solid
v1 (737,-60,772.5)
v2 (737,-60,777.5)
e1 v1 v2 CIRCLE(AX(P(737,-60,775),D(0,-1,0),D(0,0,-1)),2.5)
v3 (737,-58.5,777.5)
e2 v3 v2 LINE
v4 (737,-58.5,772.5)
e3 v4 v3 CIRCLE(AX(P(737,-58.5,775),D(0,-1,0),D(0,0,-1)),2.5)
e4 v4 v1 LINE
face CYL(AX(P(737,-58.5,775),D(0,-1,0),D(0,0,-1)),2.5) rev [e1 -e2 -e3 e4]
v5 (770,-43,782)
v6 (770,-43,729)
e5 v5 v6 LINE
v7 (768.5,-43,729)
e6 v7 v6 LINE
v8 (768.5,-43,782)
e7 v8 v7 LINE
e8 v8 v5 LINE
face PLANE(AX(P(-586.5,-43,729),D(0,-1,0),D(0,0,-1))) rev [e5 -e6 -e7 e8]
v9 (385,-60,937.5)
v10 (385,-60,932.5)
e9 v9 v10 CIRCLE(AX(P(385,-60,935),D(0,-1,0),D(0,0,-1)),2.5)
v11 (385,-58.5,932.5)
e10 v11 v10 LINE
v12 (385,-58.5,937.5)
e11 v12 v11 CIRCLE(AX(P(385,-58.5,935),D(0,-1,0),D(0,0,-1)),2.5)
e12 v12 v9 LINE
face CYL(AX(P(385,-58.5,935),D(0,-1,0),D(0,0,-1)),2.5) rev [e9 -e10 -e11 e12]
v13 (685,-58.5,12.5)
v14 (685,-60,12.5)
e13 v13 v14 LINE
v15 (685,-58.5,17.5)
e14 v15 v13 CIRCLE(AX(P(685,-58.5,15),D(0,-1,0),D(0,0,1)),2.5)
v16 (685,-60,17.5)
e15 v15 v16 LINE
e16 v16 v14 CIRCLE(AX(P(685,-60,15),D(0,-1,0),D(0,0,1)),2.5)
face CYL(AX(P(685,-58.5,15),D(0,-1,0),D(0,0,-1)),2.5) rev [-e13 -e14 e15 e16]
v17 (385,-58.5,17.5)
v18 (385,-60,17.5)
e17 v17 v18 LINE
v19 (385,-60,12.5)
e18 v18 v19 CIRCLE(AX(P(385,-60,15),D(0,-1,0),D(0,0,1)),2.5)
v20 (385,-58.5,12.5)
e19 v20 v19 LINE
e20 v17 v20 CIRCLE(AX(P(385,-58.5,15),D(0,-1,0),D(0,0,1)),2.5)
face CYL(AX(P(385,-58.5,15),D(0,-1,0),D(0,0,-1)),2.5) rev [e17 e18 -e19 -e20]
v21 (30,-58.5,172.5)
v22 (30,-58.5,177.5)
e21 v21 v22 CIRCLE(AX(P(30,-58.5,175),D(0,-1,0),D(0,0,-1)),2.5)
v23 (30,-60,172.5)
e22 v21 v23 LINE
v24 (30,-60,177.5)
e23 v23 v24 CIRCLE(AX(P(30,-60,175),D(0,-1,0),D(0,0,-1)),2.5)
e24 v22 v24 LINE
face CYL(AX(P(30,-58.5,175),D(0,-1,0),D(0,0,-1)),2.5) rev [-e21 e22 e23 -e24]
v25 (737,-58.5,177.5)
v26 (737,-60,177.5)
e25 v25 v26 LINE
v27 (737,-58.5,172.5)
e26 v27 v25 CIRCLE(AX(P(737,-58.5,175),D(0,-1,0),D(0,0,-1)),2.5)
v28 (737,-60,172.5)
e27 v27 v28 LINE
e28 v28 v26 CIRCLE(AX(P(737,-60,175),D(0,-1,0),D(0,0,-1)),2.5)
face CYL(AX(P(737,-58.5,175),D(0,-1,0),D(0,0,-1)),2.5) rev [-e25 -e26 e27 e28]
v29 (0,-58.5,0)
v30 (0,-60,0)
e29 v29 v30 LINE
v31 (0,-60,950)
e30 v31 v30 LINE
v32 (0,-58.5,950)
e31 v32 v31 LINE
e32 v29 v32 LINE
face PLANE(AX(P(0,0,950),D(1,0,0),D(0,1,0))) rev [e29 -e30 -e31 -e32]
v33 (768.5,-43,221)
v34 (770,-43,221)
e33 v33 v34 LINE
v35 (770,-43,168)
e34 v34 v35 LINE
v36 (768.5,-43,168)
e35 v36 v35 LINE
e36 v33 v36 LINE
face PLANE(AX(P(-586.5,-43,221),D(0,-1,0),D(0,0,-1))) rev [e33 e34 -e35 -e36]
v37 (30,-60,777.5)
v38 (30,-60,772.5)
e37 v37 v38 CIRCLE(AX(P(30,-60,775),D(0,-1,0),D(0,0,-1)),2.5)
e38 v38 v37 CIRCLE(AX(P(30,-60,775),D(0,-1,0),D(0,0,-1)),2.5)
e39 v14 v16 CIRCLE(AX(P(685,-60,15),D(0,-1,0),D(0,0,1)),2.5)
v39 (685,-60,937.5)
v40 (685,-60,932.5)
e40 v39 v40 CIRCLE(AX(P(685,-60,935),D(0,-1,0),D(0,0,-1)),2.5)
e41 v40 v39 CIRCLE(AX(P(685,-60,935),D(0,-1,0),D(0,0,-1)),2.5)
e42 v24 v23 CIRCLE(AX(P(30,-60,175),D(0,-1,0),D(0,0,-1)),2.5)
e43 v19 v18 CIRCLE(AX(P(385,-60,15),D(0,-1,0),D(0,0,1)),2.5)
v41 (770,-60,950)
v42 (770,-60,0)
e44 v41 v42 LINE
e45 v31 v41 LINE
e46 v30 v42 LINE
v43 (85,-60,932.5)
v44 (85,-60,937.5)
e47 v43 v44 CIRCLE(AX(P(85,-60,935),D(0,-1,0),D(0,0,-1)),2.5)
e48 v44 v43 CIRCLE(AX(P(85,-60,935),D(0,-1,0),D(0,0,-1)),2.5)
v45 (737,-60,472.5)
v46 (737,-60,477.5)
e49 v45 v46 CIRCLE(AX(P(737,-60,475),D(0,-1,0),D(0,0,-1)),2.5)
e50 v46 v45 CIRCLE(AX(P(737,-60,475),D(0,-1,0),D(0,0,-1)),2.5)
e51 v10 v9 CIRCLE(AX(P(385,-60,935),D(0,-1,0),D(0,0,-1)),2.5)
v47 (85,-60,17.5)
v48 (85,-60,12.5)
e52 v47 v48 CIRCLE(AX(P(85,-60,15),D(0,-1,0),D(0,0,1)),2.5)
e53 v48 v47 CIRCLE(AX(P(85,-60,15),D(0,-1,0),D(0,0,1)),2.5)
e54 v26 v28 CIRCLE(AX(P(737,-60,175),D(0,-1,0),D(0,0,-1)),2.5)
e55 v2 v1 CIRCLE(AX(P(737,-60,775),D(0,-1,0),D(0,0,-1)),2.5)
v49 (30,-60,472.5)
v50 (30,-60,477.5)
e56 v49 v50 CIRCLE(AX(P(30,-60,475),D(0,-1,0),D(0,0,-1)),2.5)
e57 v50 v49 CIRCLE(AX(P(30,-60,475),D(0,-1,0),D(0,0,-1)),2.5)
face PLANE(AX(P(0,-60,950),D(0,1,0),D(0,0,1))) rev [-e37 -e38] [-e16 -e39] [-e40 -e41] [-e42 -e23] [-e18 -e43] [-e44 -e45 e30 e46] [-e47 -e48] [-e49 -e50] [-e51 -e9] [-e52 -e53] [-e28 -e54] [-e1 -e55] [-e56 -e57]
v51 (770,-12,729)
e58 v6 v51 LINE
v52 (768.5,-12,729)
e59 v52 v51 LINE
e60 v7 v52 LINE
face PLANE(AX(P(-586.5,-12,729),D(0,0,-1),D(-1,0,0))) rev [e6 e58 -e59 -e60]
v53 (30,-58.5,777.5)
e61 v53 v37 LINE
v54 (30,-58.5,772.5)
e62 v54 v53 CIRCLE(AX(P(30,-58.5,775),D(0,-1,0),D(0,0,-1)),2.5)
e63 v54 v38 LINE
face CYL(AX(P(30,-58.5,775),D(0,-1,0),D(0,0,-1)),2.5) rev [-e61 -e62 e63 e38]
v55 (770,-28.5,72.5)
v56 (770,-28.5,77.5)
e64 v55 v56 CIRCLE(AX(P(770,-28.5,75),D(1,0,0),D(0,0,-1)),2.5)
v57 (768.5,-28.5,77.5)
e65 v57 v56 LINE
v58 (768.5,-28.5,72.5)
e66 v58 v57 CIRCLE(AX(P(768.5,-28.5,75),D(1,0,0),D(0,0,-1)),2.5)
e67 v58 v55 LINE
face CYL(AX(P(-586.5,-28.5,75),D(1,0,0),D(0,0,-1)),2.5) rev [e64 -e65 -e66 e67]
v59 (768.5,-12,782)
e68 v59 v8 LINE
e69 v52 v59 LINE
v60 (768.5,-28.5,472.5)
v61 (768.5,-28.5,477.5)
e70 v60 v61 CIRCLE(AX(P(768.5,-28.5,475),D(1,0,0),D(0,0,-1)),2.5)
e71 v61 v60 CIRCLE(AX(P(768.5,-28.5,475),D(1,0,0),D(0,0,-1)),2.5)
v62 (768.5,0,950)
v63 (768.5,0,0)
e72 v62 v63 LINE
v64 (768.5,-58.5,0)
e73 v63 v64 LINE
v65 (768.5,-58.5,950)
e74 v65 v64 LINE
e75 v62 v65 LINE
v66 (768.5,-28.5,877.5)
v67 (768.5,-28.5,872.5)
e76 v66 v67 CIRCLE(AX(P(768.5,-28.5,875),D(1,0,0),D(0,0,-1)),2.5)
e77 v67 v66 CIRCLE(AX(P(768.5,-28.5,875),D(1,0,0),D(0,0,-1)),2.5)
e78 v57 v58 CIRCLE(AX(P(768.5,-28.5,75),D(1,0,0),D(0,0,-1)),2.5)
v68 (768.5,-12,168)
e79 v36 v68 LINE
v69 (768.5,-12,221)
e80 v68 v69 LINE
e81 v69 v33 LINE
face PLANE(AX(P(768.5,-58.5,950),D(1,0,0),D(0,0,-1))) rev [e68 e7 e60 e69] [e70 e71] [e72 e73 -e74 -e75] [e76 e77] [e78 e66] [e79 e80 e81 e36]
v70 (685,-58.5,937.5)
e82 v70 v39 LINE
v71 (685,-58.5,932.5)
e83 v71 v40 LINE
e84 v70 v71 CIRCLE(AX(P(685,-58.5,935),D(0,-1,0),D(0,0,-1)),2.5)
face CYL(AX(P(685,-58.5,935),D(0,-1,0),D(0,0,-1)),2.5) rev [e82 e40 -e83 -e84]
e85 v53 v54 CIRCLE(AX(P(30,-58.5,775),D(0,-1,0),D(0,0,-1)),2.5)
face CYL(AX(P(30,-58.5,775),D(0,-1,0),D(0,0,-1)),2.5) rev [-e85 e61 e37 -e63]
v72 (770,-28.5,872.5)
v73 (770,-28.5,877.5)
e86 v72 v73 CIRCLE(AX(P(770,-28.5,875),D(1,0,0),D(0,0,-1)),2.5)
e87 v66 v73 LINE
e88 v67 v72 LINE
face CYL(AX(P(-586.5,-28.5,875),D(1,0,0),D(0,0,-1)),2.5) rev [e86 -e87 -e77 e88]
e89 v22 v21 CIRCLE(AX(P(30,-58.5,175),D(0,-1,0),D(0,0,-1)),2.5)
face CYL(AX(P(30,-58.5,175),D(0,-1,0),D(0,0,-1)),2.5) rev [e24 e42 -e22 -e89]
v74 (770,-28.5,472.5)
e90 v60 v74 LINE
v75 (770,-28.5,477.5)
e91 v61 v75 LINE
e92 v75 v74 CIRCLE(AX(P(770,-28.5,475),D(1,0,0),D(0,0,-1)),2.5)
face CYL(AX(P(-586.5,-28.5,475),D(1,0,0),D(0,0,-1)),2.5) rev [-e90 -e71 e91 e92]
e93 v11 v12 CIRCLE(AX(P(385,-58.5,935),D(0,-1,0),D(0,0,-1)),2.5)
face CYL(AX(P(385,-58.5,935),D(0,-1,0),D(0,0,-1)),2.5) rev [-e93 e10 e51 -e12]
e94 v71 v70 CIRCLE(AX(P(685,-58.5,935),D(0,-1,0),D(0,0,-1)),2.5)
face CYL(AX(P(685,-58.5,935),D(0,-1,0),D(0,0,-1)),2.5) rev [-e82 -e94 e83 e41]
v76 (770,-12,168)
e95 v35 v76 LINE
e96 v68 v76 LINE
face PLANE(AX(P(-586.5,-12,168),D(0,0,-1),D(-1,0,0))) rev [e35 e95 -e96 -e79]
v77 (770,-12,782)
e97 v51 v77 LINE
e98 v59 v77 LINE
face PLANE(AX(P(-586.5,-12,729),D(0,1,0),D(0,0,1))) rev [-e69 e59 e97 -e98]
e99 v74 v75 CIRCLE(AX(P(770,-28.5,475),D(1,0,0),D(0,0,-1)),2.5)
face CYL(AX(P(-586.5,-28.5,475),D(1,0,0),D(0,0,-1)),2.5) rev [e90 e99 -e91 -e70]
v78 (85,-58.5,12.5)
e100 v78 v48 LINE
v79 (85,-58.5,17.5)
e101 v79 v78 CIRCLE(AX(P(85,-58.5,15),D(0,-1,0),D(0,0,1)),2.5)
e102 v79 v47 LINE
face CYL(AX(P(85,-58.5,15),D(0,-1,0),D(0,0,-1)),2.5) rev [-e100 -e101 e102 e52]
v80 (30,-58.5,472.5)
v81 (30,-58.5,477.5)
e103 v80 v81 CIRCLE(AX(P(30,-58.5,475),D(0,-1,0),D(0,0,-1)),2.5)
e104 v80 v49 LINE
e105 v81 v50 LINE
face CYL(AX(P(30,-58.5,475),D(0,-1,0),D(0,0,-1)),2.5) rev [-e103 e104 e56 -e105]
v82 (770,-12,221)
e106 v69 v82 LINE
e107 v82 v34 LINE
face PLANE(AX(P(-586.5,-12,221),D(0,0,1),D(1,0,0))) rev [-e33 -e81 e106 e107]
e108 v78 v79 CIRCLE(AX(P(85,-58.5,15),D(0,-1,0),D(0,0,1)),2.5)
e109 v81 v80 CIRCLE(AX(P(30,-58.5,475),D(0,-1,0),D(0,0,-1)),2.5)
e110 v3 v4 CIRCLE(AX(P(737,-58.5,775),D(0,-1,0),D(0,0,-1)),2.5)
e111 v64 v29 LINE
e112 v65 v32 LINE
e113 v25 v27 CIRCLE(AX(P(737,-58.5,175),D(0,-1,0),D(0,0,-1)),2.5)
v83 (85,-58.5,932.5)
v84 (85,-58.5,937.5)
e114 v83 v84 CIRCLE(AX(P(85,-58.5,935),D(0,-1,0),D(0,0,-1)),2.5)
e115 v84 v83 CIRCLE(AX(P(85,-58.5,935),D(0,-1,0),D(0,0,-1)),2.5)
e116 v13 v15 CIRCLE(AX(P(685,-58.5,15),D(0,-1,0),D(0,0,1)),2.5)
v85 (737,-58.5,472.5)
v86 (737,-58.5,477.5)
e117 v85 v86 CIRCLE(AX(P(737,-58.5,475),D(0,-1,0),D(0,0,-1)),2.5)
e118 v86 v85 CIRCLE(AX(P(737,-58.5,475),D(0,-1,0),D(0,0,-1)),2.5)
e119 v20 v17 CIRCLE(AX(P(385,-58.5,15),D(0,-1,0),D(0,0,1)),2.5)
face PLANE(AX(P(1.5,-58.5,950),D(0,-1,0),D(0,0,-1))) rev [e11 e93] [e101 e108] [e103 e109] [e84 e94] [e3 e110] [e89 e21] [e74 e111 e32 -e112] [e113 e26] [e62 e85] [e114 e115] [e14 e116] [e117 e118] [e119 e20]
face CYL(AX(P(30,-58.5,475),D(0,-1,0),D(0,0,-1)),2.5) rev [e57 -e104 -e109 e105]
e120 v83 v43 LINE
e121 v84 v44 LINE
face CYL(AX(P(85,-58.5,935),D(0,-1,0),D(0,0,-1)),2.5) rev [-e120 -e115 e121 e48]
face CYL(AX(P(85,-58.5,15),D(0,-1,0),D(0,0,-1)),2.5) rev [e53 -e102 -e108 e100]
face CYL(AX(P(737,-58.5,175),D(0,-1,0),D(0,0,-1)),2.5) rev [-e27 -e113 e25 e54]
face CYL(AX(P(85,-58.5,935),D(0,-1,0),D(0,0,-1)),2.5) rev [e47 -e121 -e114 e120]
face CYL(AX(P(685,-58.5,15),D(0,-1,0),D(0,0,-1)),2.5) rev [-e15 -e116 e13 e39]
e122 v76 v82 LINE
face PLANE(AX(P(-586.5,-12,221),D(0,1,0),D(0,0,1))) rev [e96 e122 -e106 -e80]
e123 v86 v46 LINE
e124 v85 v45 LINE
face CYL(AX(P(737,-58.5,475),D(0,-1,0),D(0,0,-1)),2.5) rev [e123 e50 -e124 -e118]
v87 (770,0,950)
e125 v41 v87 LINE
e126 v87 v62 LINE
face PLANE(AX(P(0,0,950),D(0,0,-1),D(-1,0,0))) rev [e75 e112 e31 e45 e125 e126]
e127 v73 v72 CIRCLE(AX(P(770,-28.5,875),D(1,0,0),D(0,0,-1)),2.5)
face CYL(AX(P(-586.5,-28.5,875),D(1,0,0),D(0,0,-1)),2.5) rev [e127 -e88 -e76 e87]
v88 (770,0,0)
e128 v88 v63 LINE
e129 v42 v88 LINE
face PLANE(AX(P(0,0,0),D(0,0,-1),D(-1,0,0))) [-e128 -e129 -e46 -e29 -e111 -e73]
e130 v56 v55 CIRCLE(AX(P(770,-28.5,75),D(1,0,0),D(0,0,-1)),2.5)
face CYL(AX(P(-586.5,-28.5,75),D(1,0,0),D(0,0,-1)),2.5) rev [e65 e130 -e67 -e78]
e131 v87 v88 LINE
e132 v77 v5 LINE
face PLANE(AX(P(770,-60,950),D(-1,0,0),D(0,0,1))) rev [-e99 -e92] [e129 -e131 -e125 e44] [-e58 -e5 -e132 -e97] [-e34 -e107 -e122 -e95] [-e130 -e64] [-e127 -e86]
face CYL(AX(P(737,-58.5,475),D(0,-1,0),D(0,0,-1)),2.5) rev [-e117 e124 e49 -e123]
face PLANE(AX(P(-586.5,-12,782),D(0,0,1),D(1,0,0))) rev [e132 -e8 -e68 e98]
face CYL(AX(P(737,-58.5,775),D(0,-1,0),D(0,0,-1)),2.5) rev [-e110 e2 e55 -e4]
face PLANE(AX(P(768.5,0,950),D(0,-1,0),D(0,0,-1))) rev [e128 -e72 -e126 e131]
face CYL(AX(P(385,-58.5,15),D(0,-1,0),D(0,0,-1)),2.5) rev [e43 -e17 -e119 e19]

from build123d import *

# Parameters (mm, degrees)
BOSS_EXTRUDE1_DEPTH = 950
SKETCH2_R           = 2.5
SKETCH2_W           = 53
SKETCH2_H           = 31
CUT_EXTRUDE1_DEPTH  = 1356.5
SKETCH3_R           = 2.5
CUT_EXTRUDE2_DEPTH  = 1.5
SKETCH4_W           = 1.5
SKETCH4_H           = 950
CUT_EXTRUDE3_DEPTH  = 58.5


with BuildPart() as part:
    # Sketch1 → Boss-Extrude1 (new body)
    with BuildSketch(Plane.XY):
        Polygon((0, 0), (0, -60), (770, -60), (770, 0), (768.5, 0), (768.5, -58.5), (1.5, -58.5), (1.5, 0), align=None)
    extrude(amount=BOSS_EXTRUDE1_DEPTH)

    # Sketch2 → Cut-Extrude1 (cut)
    with BuildSketch(Plane(origin=(770, 0, 0), x_dir=(0, 0, -1), z_dir=(1, 0, 0))):
        with Locations(Location((-75, -28.5, 0), (0, 0, 270))):
            Circle(SKETCH2_R)
        with Locations(Location((-475, -28.5, 0), (0, 0, 270))):
            Circle(SKETCH2_R)
        with Locations(Location((-875, -28.5, 0), (0, 0, 270))):
            Circle(SKETCH2_R)
        with Locations((-194.5, -27.5)):
            Rectangle(SKETCH2_W, SKETCH2_H)
        with Locations((-755.5, -27.5)):
            Rectangle(SKETCH2_W, SKETCH2_H)
    extrude(amount=-CUT_EXTRUDE1_DEPTH, mode=Mode.SUBTRACT)

    # Sketch3 → Cut-Extrude2 (cut)
    with BuildSketch(Plane.XZ.offset(60)):
        with Locations(Location((737, 475, 0), (0, 0, 270))):
            Circle(SKETCH3_R)
        with Locations(Location((737, 775, 0), (0, 0, 270))):
            Circle(SKETCH3_R)
        with Locations(Location((737, 175, 0), (0, 0, 270))):
            Circle(SKETCH3_R)
        with Locations(Location((30, 775, 0), (0, 0, 270))):
            Circle(SKETCH3_R)
        with Locations(Location((30, 475, 0), (0, 0, 270))):
            Circle(SKETCH3_R)
        with Locations(Location((30, 175, 0), (0, 0, 270))):
            Circle(SKETCH3_R)
        with Locations(Location((385, 935, 0), (0, 0, 270))):
            Circle(SKETCH3_R)
        with Locations(Location((685, 935, 0), (0, 0, 270))):
            Circle(SKETCH3_R)
        with Locations(Location((85, 935, 0), (0, 0, 270))):
            Circle(SKETCH3_R)
        with Locations(Location((85, 15, 0), (0, 0, 90))):
            Circle(SKETCH3_R)
        with Locations(Location((685, 15, 0), (0, 0, 90))):
            Circle(SKETCH3_R)
        with Locations(Location((385, 15, 0), (0, 0, 90))):
            Circle(SKETCH3_R)
    extrude(amount=-CUT_EXTRUDE2_DEPTH, mode=Mode.SUBTRACT)

    # Sketch4 → Cut-Extrude3 (cut)
    with BuildSketch(Plane(origin=(0, 0, 0), x_dir=(1, 0, 0), z_dir=(0, 1, 0))):
        with Locations((0.75, -475)):
            Rectangle(SKETCH4_W, SKETCH4_H)
    extrude(amount=-CUT_EXTRUDE3_DEPTH, mode=Mode.SUBTRACT)


solid = part.part
